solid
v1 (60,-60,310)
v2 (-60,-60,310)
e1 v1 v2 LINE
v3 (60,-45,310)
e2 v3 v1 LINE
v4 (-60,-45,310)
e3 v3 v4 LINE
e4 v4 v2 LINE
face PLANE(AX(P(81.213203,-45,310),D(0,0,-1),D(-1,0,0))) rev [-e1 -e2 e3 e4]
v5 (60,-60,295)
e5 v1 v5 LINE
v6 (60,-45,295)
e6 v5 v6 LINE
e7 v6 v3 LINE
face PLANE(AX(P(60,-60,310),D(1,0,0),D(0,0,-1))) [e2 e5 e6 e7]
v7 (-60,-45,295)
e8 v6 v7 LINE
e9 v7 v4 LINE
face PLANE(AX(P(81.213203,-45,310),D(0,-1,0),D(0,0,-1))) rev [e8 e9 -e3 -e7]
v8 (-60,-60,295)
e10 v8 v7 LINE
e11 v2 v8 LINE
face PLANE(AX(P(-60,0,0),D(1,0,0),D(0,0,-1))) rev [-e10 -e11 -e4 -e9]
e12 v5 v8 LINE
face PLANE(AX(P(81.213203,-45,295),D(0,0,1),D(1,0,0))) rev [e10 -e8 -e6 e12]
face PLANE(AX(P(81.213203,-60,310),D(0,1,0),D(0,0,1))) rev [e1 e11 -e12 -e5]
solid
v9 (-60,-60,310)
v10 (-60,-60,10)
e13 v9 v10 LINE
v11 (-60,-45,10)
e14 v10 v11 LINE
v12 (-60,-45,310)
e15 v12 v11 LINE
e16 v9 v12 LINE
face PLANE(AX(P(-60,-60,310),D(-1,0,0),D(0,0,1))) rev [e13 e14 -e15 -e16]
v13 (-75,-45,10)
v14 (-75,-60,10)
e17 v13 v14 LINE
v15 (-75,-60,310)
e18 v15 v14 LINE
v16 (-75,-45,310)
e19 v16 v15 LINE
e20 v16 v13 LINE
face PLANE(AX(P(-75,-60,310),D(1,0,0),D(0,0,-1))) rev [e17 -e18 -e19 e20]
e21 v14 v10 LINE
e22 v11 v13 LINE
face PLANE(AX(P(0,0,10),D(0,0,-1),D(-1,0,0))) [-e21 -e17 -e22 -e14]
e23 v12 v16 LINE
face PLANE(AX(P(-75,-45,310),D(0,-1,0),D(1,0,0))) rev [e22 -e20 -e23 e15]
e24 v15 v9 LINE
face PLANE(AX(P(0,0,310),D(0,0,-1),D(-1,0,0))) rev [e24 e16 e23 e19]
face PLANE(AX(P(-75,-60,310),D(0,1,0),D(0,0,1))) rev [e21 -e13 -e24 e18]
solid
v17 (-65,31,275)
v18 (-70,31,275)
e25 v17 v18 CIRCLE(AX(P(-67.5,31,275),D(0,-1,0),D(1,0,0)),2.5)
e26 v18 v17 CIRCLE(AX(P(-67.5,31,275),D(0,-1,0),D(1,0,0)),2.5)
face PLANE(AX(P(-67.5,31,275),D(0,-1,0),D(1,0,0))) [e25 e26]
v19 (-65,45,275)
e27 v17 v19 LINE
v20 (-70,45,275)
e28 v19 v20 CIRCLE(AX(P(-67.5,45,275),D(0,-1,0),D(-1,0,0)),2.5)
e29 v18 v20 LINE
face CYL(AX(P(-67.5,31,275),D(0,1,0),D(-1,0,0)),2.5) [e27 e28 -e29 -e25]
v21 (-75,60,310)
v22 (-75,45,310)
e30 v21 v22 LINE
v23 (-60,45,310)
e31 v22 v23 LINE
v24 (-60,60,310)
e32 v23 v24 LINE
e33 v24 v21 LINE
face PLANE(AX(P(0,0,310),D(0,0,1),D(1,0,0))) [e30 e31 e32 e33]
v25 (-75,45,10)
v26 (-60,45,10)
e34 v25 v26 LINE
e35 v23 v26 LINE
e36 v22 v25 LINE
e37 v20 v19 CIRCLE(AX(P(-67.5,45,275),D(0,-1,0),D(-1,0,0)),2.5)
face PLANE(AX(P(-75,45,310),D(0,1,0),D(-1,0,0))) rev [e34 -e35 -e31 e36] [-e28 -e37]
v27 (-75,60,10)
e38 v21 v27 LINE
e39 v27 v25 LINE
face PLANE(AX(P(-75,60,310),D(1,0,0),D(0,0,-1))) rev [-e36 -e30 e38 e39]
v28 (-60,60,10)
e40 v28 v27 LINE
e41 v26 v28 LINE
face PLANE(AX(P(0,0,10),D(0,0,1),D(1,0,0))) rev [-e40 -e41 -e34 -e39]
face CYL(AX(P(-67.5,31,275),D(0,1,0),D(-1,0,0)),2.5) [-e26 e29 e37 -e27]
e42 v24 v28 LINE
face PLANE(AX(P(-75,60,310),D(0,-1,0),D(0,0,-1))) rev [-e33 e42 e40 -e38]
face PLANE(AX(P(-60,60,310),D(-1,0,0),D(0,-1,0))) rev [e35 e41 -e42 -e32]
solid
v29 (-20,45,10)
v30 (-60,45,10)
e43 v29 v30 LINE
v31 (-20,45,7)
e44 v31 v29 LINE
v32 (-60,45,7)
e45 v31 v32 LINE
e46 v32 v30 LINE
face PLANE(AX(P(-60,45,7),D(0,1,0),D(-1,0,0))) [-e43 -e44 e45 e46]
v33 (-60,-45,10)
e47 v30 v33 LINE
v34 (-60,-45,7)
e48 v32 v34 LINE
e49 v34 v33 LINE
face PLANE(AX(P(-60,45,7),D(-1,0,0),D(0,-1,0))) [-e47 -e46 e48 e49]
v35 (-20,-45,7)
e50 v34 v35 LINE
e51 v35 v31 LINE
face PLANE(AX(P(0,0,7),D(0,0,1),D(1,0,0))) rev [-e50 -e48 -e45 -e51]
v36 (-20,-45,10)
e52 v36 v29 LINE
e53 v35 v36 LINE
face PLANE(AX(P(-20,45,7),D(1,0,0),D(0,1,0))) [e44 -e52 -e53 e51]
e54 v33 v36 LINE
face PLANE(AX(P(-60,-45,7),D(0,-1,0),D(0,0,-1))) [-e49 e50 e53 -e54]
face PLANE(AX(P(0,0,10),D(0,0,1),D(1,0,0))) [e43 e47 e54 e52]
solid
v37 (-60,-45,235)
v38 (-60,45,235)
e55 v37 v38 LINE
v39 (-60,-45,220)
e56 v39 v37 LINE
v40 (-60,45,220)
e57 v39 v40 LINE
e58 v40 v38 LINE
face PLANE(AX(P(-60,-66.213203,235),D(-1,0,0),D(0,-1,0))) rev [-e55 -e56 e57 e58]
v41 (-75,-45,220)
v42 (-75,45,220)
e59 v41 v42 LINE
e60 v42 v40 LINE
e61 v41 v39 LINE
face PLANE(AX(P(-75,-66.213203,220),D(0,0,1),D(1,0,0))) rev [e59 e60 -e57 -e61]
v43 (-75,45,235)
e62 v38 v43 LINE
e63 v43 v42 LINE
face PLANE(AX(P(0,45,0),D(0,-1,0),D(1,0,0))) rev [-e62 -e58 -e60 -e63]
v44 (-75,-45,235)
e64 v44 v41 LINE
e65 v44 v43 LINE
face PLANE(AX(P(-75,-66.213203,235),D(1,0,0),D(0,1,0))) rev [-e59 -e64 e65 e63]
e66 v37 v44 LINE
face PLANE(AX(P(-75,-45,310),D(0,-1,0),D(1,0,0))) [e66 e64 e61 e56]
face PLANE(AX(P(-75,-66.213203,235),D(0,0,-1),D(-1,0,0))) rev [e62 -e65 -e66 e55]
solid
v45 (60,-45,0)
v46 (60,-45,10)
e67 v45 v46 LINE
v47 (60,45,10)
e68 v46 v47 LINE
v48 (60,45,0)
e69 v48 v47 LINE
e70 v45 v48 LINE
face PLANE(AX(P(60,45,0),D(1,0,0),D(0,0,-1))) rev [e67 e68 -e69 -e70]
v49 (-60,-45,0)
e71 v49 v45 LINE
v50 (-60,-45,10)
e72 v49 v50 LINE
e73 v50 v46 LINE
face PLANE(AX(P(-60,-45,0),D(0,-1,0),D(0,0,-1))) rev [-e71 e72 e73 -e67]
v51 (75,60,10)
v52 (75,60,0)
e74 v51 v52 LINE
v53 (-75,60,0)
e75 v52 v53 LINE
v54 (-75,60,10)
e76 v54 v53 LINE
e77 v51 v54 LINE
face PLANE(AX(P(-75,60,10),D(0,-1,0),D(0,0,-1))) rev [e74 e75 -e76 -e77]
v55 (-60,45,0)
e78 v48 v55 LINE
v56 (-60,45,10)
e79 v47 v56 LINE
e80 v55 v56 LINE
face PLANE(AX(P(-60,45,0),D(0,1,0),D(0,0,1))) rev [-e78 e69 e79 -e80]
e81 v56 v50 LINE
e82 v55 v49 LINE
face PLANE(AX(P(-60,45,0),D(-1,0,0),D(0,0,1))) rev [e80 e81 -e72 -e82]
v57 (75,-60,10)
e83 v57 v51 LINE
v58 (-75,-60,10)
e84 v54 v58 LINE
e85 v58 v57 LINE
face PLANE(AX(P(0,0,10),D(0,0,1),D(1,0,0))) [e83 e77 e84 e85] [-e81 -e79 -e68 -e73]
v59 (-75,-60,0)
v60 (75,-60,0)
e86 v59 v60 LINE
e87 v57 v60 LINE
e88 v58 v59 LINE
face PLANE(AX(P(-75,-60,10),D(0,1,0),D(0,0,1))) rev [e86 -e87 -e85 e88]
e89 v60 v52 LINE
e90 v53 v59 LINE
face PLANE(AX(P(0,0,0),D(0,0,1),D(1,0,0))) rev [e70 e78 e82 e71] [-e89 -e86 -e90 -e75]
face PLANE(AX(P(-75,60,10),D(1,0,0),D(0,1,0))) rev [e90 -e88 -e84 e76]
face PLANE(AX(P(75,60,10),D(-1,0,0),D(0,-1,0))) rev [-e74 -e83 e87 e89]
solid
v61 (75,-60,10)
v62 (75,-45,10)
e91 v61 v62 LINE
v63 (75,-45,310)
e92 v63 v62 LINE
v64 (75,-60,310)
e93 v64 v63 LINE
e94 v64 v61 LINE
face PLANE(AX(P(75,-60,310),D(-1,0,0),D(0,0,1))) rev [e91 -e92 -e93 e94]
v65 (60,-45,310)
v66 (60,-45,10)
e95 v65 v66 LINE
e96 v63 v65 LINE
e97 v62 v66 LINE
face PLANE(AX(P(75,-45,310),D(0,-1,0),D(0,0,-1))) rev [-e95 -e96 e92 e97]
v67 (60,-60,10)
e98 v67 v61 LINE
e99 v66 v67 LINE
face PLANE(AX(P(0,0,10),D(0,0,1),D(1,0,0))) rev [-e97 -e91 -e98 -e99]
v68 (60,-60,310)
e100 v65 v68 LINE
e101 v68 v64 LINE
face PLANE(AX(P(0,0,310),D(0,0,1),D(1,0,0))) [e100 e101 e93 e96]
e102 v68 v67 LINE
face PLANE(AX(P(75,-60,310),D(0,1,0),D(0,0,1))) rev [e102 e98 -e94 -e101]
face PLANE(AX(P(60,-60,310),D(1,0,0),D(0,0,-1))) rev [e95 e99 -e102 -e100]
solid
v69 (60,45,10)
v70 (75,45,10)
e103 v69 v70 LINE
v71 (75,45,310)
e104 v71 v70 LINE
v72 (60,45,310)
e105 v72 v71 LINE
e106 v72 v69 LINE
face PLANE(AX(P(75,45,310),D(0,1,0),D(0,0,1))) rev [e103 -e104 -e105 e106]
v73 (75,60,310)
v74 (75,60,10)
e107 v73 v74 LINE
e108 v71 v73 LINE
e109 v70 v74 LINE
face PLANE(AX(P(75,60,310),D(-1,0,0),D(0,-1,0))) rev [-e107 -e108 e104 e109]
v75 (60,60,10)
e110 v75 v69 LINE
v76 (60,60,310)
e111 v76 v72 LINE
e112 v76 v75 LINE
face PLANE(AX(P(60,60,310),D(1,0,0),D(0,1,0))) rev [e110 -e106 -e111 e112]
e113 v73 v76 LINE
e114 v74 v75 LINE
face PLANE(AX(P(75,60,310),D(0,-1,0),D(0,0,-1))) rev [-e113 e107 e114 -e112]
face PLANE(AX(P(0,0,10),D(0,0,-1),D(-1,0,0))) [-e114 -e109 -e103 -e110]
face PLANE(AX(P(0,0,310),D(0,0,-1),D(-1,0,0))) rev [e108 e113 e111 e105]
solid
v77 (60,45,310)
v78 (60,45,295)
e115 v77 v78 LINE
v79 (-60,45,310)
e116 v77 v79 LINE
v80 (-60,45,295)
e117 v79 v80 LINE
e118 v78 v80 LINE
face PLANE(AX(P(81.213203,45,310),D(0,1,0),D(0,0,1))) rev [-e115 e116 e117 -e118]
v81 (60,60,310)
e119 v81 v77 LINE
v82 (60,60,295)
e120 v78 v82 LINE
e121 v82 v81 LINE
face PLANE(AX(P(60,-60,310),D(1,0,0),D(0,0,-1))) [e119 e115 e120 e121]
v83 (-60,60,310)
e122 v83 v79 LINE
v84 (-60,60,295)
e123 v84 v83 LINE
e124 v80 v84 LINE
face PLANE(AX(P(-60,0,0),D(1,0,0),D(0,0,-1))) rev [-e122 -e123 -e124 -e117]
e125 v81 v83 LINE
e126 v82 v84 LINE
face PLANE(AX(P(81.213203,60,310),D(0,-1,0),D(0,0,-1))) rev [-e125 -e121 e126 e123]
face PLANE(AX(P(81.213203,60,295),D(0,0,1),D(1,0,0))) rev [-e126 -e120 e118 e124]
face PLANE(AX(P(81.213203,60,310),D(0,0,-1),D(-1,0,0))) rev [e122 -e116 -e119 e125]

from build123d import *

# Parameters (mm, degrees)
SKETCH2_W               = 150
SKETCH2_H               = 120
BOSS_EXTRUDE1_DEPTH     = 10
CUT_EXTRUDE4_DEPTH      = 97.566039579
CUT_EXTRUDE4_DEPTH_BACK = 97.566039579
SKETCH6_W               = 120
SKETCH6_H               = 90
SKETCH7_W               = 15
SKETCH7_H               = 15
BOSS_EXTRUDE2_DEPTH     = 300
BOSS_EXTRUDE2_2_DEPTH   = 300
BOSS_EXTRUDE2_3_DEPTH   = 300
BOSS_EXTRUDE2_4_DEPTH   = 300
SKETCH14_W              = 15
SKETCH14_H              = 15
BOSS_EXTRUDE7_DEPTH     = 120
BOSS_EXTRUDE7_2_DEPTH   = 120
SKETCH15_W              = 15
SKETCH15_H              = 15
BOSS_EXTRUDE8_DEPTH     = 90
SKETCH16_R              = 2.5
BOSS_EXTRUDE9_DEPTH     = 14
SKETCH17_W              = 40
SKETCH17_H              = 90
BOSS_EXTRUDE10_DEPTH    = 3


with BuildPart() as part:
    # Sketch2 → Boss-Extrude1 (new body)
    with BuildSketch(Plane.XY):
        Rectangle(SKETCH2_W, SKETCH2_H)
    extrude(amount=BOSS_EXTRUDE1_DEPTH)

    # Sketch6 → Cut-Extrude4 (cut, two sides: drawn at the far end of the back side and taken through both)
    with BuildSketch(Plane.XY.offset(10).offset(-CUT_EXTRUDE4_DEPTH_BACK)):
        Rectangle(SKETCH6_W, SKETCH6_H)
    extrude(amount=CUT_EXTRUDE4_DEPTH + CUT_EXTRUDE4_DEPTH_BACK, mode=Mode.SUBTRACT)


with BuildPart() as body_2:
    # Sketch7 → Boss-Extrude2 (new body)
    with BuildSketch(Plane.XY.offset(10)):
        with Locations((-67.5, 52.5)):
            Rectangle(SKETCH7_W, SKETCH7_H)
    extrude(amount=BOSS_EXTRUDE2_DEPTH)

    # Sketch16 → Boss-Extrude9 (add)
    with BuildSketch(Plane.XZ.offset(-45)):
        with Locations(Location((-67.5, 275, 0), (0, 0, 180))):
            Circle(SKETCH16_R)
    extrude(amount=BOSS_EXTRUDE9_DEPTH)


with BuildPart() as body_3:
    # Sketch7 → Boss-Extrude2 2 (new body)
    with BuildSketch(Plane.XY.offset(10)):
        with Locations((-67.5, -52.5)):
            Rectangle(SKETCH7_W, SKETCH7_H)
    extrude(amount=BOSS_EXTRUDE2_2_DEPTH)


with BuildPart() as body_4:
    # Sketch7 → Boss-Extrude2 3 (new body)
    with BuildSketch(Plane.XY.offset(10)):
        with Locations((67.5, 52.5)):
            Rectangle(SKETCH7_W, SKETCH7_H)
    extrude(amount=BOSS_EXTRUDE2_3_DEPTH)


with BuildPart() as body_5:
    # Sketch7 → Boss-Extrude2 4 (new body)
    with BuildSketch(Plane.XY.offset(10)):
        with Locations((67.5, -52.5)):
            Rectangle(SKETCH7_W, SKETCH7_H)
    extrude(amount=BOSS_EXTRUDE2_4_DEPTH)


with BuildPart() as body_6:
    # Sketch14 → Boss-Extrude7 (new body)
    with BuildSketch(Plane(origin=(-60, 0, 0), x_dir=(0, 0, -1), z_dir=(1, 0, 0))):
        with Locations((-302.5, 52.5)):
            Rectangle(SKETCH14_W, SKETCH14_H)
    extrude(amount=BOSS_EXTRUDE7_DEPTH)


with BuildPart() as body_7:
    # Sketch14 → Boss-Extrude7 2 (new body)
    with BuildSketch(Plane(origin=(-60, 0, 0), x_dir=(0, 0, -1), z_dir=(1, 0, 0))):
        with Locations((-302.5, -52.5)):
            Rectangle(SKETCH14_W, SKETCH14_H)
    extrude(amount=BOSS_EXTRUDE7_2_DEPTH)


with BuildPart() as body_8:
    # Sketch15 → Boss-Extrude8 (new body)
    with BuildSketch(Plane.XZ.offset(-45)):
        with Locations((-67.5, 227.5)):
            Rectangle(SKETCH15_W, SKETCH15_H)
    extrude(amount=BOSS_EXTRUDE8_DEPTH)


with BuildPart() as body_9:
    # Sketch17 → Boss-Extrude10 (new body)
    with BuildSketch(Plane.XY.offset(10)):
        with Locations((-40, 0)):
            Rectangle(SKETCH17_W, SKETCH17_H)
    extrude(amount=-BOSS_EXTRUDE10_DEPTH)


solid = Compound([part.part, body_2.part, body_3.part, body_4.part, body_5.part, body_6.part, body_7.part, body_8.part, body_9.part])
